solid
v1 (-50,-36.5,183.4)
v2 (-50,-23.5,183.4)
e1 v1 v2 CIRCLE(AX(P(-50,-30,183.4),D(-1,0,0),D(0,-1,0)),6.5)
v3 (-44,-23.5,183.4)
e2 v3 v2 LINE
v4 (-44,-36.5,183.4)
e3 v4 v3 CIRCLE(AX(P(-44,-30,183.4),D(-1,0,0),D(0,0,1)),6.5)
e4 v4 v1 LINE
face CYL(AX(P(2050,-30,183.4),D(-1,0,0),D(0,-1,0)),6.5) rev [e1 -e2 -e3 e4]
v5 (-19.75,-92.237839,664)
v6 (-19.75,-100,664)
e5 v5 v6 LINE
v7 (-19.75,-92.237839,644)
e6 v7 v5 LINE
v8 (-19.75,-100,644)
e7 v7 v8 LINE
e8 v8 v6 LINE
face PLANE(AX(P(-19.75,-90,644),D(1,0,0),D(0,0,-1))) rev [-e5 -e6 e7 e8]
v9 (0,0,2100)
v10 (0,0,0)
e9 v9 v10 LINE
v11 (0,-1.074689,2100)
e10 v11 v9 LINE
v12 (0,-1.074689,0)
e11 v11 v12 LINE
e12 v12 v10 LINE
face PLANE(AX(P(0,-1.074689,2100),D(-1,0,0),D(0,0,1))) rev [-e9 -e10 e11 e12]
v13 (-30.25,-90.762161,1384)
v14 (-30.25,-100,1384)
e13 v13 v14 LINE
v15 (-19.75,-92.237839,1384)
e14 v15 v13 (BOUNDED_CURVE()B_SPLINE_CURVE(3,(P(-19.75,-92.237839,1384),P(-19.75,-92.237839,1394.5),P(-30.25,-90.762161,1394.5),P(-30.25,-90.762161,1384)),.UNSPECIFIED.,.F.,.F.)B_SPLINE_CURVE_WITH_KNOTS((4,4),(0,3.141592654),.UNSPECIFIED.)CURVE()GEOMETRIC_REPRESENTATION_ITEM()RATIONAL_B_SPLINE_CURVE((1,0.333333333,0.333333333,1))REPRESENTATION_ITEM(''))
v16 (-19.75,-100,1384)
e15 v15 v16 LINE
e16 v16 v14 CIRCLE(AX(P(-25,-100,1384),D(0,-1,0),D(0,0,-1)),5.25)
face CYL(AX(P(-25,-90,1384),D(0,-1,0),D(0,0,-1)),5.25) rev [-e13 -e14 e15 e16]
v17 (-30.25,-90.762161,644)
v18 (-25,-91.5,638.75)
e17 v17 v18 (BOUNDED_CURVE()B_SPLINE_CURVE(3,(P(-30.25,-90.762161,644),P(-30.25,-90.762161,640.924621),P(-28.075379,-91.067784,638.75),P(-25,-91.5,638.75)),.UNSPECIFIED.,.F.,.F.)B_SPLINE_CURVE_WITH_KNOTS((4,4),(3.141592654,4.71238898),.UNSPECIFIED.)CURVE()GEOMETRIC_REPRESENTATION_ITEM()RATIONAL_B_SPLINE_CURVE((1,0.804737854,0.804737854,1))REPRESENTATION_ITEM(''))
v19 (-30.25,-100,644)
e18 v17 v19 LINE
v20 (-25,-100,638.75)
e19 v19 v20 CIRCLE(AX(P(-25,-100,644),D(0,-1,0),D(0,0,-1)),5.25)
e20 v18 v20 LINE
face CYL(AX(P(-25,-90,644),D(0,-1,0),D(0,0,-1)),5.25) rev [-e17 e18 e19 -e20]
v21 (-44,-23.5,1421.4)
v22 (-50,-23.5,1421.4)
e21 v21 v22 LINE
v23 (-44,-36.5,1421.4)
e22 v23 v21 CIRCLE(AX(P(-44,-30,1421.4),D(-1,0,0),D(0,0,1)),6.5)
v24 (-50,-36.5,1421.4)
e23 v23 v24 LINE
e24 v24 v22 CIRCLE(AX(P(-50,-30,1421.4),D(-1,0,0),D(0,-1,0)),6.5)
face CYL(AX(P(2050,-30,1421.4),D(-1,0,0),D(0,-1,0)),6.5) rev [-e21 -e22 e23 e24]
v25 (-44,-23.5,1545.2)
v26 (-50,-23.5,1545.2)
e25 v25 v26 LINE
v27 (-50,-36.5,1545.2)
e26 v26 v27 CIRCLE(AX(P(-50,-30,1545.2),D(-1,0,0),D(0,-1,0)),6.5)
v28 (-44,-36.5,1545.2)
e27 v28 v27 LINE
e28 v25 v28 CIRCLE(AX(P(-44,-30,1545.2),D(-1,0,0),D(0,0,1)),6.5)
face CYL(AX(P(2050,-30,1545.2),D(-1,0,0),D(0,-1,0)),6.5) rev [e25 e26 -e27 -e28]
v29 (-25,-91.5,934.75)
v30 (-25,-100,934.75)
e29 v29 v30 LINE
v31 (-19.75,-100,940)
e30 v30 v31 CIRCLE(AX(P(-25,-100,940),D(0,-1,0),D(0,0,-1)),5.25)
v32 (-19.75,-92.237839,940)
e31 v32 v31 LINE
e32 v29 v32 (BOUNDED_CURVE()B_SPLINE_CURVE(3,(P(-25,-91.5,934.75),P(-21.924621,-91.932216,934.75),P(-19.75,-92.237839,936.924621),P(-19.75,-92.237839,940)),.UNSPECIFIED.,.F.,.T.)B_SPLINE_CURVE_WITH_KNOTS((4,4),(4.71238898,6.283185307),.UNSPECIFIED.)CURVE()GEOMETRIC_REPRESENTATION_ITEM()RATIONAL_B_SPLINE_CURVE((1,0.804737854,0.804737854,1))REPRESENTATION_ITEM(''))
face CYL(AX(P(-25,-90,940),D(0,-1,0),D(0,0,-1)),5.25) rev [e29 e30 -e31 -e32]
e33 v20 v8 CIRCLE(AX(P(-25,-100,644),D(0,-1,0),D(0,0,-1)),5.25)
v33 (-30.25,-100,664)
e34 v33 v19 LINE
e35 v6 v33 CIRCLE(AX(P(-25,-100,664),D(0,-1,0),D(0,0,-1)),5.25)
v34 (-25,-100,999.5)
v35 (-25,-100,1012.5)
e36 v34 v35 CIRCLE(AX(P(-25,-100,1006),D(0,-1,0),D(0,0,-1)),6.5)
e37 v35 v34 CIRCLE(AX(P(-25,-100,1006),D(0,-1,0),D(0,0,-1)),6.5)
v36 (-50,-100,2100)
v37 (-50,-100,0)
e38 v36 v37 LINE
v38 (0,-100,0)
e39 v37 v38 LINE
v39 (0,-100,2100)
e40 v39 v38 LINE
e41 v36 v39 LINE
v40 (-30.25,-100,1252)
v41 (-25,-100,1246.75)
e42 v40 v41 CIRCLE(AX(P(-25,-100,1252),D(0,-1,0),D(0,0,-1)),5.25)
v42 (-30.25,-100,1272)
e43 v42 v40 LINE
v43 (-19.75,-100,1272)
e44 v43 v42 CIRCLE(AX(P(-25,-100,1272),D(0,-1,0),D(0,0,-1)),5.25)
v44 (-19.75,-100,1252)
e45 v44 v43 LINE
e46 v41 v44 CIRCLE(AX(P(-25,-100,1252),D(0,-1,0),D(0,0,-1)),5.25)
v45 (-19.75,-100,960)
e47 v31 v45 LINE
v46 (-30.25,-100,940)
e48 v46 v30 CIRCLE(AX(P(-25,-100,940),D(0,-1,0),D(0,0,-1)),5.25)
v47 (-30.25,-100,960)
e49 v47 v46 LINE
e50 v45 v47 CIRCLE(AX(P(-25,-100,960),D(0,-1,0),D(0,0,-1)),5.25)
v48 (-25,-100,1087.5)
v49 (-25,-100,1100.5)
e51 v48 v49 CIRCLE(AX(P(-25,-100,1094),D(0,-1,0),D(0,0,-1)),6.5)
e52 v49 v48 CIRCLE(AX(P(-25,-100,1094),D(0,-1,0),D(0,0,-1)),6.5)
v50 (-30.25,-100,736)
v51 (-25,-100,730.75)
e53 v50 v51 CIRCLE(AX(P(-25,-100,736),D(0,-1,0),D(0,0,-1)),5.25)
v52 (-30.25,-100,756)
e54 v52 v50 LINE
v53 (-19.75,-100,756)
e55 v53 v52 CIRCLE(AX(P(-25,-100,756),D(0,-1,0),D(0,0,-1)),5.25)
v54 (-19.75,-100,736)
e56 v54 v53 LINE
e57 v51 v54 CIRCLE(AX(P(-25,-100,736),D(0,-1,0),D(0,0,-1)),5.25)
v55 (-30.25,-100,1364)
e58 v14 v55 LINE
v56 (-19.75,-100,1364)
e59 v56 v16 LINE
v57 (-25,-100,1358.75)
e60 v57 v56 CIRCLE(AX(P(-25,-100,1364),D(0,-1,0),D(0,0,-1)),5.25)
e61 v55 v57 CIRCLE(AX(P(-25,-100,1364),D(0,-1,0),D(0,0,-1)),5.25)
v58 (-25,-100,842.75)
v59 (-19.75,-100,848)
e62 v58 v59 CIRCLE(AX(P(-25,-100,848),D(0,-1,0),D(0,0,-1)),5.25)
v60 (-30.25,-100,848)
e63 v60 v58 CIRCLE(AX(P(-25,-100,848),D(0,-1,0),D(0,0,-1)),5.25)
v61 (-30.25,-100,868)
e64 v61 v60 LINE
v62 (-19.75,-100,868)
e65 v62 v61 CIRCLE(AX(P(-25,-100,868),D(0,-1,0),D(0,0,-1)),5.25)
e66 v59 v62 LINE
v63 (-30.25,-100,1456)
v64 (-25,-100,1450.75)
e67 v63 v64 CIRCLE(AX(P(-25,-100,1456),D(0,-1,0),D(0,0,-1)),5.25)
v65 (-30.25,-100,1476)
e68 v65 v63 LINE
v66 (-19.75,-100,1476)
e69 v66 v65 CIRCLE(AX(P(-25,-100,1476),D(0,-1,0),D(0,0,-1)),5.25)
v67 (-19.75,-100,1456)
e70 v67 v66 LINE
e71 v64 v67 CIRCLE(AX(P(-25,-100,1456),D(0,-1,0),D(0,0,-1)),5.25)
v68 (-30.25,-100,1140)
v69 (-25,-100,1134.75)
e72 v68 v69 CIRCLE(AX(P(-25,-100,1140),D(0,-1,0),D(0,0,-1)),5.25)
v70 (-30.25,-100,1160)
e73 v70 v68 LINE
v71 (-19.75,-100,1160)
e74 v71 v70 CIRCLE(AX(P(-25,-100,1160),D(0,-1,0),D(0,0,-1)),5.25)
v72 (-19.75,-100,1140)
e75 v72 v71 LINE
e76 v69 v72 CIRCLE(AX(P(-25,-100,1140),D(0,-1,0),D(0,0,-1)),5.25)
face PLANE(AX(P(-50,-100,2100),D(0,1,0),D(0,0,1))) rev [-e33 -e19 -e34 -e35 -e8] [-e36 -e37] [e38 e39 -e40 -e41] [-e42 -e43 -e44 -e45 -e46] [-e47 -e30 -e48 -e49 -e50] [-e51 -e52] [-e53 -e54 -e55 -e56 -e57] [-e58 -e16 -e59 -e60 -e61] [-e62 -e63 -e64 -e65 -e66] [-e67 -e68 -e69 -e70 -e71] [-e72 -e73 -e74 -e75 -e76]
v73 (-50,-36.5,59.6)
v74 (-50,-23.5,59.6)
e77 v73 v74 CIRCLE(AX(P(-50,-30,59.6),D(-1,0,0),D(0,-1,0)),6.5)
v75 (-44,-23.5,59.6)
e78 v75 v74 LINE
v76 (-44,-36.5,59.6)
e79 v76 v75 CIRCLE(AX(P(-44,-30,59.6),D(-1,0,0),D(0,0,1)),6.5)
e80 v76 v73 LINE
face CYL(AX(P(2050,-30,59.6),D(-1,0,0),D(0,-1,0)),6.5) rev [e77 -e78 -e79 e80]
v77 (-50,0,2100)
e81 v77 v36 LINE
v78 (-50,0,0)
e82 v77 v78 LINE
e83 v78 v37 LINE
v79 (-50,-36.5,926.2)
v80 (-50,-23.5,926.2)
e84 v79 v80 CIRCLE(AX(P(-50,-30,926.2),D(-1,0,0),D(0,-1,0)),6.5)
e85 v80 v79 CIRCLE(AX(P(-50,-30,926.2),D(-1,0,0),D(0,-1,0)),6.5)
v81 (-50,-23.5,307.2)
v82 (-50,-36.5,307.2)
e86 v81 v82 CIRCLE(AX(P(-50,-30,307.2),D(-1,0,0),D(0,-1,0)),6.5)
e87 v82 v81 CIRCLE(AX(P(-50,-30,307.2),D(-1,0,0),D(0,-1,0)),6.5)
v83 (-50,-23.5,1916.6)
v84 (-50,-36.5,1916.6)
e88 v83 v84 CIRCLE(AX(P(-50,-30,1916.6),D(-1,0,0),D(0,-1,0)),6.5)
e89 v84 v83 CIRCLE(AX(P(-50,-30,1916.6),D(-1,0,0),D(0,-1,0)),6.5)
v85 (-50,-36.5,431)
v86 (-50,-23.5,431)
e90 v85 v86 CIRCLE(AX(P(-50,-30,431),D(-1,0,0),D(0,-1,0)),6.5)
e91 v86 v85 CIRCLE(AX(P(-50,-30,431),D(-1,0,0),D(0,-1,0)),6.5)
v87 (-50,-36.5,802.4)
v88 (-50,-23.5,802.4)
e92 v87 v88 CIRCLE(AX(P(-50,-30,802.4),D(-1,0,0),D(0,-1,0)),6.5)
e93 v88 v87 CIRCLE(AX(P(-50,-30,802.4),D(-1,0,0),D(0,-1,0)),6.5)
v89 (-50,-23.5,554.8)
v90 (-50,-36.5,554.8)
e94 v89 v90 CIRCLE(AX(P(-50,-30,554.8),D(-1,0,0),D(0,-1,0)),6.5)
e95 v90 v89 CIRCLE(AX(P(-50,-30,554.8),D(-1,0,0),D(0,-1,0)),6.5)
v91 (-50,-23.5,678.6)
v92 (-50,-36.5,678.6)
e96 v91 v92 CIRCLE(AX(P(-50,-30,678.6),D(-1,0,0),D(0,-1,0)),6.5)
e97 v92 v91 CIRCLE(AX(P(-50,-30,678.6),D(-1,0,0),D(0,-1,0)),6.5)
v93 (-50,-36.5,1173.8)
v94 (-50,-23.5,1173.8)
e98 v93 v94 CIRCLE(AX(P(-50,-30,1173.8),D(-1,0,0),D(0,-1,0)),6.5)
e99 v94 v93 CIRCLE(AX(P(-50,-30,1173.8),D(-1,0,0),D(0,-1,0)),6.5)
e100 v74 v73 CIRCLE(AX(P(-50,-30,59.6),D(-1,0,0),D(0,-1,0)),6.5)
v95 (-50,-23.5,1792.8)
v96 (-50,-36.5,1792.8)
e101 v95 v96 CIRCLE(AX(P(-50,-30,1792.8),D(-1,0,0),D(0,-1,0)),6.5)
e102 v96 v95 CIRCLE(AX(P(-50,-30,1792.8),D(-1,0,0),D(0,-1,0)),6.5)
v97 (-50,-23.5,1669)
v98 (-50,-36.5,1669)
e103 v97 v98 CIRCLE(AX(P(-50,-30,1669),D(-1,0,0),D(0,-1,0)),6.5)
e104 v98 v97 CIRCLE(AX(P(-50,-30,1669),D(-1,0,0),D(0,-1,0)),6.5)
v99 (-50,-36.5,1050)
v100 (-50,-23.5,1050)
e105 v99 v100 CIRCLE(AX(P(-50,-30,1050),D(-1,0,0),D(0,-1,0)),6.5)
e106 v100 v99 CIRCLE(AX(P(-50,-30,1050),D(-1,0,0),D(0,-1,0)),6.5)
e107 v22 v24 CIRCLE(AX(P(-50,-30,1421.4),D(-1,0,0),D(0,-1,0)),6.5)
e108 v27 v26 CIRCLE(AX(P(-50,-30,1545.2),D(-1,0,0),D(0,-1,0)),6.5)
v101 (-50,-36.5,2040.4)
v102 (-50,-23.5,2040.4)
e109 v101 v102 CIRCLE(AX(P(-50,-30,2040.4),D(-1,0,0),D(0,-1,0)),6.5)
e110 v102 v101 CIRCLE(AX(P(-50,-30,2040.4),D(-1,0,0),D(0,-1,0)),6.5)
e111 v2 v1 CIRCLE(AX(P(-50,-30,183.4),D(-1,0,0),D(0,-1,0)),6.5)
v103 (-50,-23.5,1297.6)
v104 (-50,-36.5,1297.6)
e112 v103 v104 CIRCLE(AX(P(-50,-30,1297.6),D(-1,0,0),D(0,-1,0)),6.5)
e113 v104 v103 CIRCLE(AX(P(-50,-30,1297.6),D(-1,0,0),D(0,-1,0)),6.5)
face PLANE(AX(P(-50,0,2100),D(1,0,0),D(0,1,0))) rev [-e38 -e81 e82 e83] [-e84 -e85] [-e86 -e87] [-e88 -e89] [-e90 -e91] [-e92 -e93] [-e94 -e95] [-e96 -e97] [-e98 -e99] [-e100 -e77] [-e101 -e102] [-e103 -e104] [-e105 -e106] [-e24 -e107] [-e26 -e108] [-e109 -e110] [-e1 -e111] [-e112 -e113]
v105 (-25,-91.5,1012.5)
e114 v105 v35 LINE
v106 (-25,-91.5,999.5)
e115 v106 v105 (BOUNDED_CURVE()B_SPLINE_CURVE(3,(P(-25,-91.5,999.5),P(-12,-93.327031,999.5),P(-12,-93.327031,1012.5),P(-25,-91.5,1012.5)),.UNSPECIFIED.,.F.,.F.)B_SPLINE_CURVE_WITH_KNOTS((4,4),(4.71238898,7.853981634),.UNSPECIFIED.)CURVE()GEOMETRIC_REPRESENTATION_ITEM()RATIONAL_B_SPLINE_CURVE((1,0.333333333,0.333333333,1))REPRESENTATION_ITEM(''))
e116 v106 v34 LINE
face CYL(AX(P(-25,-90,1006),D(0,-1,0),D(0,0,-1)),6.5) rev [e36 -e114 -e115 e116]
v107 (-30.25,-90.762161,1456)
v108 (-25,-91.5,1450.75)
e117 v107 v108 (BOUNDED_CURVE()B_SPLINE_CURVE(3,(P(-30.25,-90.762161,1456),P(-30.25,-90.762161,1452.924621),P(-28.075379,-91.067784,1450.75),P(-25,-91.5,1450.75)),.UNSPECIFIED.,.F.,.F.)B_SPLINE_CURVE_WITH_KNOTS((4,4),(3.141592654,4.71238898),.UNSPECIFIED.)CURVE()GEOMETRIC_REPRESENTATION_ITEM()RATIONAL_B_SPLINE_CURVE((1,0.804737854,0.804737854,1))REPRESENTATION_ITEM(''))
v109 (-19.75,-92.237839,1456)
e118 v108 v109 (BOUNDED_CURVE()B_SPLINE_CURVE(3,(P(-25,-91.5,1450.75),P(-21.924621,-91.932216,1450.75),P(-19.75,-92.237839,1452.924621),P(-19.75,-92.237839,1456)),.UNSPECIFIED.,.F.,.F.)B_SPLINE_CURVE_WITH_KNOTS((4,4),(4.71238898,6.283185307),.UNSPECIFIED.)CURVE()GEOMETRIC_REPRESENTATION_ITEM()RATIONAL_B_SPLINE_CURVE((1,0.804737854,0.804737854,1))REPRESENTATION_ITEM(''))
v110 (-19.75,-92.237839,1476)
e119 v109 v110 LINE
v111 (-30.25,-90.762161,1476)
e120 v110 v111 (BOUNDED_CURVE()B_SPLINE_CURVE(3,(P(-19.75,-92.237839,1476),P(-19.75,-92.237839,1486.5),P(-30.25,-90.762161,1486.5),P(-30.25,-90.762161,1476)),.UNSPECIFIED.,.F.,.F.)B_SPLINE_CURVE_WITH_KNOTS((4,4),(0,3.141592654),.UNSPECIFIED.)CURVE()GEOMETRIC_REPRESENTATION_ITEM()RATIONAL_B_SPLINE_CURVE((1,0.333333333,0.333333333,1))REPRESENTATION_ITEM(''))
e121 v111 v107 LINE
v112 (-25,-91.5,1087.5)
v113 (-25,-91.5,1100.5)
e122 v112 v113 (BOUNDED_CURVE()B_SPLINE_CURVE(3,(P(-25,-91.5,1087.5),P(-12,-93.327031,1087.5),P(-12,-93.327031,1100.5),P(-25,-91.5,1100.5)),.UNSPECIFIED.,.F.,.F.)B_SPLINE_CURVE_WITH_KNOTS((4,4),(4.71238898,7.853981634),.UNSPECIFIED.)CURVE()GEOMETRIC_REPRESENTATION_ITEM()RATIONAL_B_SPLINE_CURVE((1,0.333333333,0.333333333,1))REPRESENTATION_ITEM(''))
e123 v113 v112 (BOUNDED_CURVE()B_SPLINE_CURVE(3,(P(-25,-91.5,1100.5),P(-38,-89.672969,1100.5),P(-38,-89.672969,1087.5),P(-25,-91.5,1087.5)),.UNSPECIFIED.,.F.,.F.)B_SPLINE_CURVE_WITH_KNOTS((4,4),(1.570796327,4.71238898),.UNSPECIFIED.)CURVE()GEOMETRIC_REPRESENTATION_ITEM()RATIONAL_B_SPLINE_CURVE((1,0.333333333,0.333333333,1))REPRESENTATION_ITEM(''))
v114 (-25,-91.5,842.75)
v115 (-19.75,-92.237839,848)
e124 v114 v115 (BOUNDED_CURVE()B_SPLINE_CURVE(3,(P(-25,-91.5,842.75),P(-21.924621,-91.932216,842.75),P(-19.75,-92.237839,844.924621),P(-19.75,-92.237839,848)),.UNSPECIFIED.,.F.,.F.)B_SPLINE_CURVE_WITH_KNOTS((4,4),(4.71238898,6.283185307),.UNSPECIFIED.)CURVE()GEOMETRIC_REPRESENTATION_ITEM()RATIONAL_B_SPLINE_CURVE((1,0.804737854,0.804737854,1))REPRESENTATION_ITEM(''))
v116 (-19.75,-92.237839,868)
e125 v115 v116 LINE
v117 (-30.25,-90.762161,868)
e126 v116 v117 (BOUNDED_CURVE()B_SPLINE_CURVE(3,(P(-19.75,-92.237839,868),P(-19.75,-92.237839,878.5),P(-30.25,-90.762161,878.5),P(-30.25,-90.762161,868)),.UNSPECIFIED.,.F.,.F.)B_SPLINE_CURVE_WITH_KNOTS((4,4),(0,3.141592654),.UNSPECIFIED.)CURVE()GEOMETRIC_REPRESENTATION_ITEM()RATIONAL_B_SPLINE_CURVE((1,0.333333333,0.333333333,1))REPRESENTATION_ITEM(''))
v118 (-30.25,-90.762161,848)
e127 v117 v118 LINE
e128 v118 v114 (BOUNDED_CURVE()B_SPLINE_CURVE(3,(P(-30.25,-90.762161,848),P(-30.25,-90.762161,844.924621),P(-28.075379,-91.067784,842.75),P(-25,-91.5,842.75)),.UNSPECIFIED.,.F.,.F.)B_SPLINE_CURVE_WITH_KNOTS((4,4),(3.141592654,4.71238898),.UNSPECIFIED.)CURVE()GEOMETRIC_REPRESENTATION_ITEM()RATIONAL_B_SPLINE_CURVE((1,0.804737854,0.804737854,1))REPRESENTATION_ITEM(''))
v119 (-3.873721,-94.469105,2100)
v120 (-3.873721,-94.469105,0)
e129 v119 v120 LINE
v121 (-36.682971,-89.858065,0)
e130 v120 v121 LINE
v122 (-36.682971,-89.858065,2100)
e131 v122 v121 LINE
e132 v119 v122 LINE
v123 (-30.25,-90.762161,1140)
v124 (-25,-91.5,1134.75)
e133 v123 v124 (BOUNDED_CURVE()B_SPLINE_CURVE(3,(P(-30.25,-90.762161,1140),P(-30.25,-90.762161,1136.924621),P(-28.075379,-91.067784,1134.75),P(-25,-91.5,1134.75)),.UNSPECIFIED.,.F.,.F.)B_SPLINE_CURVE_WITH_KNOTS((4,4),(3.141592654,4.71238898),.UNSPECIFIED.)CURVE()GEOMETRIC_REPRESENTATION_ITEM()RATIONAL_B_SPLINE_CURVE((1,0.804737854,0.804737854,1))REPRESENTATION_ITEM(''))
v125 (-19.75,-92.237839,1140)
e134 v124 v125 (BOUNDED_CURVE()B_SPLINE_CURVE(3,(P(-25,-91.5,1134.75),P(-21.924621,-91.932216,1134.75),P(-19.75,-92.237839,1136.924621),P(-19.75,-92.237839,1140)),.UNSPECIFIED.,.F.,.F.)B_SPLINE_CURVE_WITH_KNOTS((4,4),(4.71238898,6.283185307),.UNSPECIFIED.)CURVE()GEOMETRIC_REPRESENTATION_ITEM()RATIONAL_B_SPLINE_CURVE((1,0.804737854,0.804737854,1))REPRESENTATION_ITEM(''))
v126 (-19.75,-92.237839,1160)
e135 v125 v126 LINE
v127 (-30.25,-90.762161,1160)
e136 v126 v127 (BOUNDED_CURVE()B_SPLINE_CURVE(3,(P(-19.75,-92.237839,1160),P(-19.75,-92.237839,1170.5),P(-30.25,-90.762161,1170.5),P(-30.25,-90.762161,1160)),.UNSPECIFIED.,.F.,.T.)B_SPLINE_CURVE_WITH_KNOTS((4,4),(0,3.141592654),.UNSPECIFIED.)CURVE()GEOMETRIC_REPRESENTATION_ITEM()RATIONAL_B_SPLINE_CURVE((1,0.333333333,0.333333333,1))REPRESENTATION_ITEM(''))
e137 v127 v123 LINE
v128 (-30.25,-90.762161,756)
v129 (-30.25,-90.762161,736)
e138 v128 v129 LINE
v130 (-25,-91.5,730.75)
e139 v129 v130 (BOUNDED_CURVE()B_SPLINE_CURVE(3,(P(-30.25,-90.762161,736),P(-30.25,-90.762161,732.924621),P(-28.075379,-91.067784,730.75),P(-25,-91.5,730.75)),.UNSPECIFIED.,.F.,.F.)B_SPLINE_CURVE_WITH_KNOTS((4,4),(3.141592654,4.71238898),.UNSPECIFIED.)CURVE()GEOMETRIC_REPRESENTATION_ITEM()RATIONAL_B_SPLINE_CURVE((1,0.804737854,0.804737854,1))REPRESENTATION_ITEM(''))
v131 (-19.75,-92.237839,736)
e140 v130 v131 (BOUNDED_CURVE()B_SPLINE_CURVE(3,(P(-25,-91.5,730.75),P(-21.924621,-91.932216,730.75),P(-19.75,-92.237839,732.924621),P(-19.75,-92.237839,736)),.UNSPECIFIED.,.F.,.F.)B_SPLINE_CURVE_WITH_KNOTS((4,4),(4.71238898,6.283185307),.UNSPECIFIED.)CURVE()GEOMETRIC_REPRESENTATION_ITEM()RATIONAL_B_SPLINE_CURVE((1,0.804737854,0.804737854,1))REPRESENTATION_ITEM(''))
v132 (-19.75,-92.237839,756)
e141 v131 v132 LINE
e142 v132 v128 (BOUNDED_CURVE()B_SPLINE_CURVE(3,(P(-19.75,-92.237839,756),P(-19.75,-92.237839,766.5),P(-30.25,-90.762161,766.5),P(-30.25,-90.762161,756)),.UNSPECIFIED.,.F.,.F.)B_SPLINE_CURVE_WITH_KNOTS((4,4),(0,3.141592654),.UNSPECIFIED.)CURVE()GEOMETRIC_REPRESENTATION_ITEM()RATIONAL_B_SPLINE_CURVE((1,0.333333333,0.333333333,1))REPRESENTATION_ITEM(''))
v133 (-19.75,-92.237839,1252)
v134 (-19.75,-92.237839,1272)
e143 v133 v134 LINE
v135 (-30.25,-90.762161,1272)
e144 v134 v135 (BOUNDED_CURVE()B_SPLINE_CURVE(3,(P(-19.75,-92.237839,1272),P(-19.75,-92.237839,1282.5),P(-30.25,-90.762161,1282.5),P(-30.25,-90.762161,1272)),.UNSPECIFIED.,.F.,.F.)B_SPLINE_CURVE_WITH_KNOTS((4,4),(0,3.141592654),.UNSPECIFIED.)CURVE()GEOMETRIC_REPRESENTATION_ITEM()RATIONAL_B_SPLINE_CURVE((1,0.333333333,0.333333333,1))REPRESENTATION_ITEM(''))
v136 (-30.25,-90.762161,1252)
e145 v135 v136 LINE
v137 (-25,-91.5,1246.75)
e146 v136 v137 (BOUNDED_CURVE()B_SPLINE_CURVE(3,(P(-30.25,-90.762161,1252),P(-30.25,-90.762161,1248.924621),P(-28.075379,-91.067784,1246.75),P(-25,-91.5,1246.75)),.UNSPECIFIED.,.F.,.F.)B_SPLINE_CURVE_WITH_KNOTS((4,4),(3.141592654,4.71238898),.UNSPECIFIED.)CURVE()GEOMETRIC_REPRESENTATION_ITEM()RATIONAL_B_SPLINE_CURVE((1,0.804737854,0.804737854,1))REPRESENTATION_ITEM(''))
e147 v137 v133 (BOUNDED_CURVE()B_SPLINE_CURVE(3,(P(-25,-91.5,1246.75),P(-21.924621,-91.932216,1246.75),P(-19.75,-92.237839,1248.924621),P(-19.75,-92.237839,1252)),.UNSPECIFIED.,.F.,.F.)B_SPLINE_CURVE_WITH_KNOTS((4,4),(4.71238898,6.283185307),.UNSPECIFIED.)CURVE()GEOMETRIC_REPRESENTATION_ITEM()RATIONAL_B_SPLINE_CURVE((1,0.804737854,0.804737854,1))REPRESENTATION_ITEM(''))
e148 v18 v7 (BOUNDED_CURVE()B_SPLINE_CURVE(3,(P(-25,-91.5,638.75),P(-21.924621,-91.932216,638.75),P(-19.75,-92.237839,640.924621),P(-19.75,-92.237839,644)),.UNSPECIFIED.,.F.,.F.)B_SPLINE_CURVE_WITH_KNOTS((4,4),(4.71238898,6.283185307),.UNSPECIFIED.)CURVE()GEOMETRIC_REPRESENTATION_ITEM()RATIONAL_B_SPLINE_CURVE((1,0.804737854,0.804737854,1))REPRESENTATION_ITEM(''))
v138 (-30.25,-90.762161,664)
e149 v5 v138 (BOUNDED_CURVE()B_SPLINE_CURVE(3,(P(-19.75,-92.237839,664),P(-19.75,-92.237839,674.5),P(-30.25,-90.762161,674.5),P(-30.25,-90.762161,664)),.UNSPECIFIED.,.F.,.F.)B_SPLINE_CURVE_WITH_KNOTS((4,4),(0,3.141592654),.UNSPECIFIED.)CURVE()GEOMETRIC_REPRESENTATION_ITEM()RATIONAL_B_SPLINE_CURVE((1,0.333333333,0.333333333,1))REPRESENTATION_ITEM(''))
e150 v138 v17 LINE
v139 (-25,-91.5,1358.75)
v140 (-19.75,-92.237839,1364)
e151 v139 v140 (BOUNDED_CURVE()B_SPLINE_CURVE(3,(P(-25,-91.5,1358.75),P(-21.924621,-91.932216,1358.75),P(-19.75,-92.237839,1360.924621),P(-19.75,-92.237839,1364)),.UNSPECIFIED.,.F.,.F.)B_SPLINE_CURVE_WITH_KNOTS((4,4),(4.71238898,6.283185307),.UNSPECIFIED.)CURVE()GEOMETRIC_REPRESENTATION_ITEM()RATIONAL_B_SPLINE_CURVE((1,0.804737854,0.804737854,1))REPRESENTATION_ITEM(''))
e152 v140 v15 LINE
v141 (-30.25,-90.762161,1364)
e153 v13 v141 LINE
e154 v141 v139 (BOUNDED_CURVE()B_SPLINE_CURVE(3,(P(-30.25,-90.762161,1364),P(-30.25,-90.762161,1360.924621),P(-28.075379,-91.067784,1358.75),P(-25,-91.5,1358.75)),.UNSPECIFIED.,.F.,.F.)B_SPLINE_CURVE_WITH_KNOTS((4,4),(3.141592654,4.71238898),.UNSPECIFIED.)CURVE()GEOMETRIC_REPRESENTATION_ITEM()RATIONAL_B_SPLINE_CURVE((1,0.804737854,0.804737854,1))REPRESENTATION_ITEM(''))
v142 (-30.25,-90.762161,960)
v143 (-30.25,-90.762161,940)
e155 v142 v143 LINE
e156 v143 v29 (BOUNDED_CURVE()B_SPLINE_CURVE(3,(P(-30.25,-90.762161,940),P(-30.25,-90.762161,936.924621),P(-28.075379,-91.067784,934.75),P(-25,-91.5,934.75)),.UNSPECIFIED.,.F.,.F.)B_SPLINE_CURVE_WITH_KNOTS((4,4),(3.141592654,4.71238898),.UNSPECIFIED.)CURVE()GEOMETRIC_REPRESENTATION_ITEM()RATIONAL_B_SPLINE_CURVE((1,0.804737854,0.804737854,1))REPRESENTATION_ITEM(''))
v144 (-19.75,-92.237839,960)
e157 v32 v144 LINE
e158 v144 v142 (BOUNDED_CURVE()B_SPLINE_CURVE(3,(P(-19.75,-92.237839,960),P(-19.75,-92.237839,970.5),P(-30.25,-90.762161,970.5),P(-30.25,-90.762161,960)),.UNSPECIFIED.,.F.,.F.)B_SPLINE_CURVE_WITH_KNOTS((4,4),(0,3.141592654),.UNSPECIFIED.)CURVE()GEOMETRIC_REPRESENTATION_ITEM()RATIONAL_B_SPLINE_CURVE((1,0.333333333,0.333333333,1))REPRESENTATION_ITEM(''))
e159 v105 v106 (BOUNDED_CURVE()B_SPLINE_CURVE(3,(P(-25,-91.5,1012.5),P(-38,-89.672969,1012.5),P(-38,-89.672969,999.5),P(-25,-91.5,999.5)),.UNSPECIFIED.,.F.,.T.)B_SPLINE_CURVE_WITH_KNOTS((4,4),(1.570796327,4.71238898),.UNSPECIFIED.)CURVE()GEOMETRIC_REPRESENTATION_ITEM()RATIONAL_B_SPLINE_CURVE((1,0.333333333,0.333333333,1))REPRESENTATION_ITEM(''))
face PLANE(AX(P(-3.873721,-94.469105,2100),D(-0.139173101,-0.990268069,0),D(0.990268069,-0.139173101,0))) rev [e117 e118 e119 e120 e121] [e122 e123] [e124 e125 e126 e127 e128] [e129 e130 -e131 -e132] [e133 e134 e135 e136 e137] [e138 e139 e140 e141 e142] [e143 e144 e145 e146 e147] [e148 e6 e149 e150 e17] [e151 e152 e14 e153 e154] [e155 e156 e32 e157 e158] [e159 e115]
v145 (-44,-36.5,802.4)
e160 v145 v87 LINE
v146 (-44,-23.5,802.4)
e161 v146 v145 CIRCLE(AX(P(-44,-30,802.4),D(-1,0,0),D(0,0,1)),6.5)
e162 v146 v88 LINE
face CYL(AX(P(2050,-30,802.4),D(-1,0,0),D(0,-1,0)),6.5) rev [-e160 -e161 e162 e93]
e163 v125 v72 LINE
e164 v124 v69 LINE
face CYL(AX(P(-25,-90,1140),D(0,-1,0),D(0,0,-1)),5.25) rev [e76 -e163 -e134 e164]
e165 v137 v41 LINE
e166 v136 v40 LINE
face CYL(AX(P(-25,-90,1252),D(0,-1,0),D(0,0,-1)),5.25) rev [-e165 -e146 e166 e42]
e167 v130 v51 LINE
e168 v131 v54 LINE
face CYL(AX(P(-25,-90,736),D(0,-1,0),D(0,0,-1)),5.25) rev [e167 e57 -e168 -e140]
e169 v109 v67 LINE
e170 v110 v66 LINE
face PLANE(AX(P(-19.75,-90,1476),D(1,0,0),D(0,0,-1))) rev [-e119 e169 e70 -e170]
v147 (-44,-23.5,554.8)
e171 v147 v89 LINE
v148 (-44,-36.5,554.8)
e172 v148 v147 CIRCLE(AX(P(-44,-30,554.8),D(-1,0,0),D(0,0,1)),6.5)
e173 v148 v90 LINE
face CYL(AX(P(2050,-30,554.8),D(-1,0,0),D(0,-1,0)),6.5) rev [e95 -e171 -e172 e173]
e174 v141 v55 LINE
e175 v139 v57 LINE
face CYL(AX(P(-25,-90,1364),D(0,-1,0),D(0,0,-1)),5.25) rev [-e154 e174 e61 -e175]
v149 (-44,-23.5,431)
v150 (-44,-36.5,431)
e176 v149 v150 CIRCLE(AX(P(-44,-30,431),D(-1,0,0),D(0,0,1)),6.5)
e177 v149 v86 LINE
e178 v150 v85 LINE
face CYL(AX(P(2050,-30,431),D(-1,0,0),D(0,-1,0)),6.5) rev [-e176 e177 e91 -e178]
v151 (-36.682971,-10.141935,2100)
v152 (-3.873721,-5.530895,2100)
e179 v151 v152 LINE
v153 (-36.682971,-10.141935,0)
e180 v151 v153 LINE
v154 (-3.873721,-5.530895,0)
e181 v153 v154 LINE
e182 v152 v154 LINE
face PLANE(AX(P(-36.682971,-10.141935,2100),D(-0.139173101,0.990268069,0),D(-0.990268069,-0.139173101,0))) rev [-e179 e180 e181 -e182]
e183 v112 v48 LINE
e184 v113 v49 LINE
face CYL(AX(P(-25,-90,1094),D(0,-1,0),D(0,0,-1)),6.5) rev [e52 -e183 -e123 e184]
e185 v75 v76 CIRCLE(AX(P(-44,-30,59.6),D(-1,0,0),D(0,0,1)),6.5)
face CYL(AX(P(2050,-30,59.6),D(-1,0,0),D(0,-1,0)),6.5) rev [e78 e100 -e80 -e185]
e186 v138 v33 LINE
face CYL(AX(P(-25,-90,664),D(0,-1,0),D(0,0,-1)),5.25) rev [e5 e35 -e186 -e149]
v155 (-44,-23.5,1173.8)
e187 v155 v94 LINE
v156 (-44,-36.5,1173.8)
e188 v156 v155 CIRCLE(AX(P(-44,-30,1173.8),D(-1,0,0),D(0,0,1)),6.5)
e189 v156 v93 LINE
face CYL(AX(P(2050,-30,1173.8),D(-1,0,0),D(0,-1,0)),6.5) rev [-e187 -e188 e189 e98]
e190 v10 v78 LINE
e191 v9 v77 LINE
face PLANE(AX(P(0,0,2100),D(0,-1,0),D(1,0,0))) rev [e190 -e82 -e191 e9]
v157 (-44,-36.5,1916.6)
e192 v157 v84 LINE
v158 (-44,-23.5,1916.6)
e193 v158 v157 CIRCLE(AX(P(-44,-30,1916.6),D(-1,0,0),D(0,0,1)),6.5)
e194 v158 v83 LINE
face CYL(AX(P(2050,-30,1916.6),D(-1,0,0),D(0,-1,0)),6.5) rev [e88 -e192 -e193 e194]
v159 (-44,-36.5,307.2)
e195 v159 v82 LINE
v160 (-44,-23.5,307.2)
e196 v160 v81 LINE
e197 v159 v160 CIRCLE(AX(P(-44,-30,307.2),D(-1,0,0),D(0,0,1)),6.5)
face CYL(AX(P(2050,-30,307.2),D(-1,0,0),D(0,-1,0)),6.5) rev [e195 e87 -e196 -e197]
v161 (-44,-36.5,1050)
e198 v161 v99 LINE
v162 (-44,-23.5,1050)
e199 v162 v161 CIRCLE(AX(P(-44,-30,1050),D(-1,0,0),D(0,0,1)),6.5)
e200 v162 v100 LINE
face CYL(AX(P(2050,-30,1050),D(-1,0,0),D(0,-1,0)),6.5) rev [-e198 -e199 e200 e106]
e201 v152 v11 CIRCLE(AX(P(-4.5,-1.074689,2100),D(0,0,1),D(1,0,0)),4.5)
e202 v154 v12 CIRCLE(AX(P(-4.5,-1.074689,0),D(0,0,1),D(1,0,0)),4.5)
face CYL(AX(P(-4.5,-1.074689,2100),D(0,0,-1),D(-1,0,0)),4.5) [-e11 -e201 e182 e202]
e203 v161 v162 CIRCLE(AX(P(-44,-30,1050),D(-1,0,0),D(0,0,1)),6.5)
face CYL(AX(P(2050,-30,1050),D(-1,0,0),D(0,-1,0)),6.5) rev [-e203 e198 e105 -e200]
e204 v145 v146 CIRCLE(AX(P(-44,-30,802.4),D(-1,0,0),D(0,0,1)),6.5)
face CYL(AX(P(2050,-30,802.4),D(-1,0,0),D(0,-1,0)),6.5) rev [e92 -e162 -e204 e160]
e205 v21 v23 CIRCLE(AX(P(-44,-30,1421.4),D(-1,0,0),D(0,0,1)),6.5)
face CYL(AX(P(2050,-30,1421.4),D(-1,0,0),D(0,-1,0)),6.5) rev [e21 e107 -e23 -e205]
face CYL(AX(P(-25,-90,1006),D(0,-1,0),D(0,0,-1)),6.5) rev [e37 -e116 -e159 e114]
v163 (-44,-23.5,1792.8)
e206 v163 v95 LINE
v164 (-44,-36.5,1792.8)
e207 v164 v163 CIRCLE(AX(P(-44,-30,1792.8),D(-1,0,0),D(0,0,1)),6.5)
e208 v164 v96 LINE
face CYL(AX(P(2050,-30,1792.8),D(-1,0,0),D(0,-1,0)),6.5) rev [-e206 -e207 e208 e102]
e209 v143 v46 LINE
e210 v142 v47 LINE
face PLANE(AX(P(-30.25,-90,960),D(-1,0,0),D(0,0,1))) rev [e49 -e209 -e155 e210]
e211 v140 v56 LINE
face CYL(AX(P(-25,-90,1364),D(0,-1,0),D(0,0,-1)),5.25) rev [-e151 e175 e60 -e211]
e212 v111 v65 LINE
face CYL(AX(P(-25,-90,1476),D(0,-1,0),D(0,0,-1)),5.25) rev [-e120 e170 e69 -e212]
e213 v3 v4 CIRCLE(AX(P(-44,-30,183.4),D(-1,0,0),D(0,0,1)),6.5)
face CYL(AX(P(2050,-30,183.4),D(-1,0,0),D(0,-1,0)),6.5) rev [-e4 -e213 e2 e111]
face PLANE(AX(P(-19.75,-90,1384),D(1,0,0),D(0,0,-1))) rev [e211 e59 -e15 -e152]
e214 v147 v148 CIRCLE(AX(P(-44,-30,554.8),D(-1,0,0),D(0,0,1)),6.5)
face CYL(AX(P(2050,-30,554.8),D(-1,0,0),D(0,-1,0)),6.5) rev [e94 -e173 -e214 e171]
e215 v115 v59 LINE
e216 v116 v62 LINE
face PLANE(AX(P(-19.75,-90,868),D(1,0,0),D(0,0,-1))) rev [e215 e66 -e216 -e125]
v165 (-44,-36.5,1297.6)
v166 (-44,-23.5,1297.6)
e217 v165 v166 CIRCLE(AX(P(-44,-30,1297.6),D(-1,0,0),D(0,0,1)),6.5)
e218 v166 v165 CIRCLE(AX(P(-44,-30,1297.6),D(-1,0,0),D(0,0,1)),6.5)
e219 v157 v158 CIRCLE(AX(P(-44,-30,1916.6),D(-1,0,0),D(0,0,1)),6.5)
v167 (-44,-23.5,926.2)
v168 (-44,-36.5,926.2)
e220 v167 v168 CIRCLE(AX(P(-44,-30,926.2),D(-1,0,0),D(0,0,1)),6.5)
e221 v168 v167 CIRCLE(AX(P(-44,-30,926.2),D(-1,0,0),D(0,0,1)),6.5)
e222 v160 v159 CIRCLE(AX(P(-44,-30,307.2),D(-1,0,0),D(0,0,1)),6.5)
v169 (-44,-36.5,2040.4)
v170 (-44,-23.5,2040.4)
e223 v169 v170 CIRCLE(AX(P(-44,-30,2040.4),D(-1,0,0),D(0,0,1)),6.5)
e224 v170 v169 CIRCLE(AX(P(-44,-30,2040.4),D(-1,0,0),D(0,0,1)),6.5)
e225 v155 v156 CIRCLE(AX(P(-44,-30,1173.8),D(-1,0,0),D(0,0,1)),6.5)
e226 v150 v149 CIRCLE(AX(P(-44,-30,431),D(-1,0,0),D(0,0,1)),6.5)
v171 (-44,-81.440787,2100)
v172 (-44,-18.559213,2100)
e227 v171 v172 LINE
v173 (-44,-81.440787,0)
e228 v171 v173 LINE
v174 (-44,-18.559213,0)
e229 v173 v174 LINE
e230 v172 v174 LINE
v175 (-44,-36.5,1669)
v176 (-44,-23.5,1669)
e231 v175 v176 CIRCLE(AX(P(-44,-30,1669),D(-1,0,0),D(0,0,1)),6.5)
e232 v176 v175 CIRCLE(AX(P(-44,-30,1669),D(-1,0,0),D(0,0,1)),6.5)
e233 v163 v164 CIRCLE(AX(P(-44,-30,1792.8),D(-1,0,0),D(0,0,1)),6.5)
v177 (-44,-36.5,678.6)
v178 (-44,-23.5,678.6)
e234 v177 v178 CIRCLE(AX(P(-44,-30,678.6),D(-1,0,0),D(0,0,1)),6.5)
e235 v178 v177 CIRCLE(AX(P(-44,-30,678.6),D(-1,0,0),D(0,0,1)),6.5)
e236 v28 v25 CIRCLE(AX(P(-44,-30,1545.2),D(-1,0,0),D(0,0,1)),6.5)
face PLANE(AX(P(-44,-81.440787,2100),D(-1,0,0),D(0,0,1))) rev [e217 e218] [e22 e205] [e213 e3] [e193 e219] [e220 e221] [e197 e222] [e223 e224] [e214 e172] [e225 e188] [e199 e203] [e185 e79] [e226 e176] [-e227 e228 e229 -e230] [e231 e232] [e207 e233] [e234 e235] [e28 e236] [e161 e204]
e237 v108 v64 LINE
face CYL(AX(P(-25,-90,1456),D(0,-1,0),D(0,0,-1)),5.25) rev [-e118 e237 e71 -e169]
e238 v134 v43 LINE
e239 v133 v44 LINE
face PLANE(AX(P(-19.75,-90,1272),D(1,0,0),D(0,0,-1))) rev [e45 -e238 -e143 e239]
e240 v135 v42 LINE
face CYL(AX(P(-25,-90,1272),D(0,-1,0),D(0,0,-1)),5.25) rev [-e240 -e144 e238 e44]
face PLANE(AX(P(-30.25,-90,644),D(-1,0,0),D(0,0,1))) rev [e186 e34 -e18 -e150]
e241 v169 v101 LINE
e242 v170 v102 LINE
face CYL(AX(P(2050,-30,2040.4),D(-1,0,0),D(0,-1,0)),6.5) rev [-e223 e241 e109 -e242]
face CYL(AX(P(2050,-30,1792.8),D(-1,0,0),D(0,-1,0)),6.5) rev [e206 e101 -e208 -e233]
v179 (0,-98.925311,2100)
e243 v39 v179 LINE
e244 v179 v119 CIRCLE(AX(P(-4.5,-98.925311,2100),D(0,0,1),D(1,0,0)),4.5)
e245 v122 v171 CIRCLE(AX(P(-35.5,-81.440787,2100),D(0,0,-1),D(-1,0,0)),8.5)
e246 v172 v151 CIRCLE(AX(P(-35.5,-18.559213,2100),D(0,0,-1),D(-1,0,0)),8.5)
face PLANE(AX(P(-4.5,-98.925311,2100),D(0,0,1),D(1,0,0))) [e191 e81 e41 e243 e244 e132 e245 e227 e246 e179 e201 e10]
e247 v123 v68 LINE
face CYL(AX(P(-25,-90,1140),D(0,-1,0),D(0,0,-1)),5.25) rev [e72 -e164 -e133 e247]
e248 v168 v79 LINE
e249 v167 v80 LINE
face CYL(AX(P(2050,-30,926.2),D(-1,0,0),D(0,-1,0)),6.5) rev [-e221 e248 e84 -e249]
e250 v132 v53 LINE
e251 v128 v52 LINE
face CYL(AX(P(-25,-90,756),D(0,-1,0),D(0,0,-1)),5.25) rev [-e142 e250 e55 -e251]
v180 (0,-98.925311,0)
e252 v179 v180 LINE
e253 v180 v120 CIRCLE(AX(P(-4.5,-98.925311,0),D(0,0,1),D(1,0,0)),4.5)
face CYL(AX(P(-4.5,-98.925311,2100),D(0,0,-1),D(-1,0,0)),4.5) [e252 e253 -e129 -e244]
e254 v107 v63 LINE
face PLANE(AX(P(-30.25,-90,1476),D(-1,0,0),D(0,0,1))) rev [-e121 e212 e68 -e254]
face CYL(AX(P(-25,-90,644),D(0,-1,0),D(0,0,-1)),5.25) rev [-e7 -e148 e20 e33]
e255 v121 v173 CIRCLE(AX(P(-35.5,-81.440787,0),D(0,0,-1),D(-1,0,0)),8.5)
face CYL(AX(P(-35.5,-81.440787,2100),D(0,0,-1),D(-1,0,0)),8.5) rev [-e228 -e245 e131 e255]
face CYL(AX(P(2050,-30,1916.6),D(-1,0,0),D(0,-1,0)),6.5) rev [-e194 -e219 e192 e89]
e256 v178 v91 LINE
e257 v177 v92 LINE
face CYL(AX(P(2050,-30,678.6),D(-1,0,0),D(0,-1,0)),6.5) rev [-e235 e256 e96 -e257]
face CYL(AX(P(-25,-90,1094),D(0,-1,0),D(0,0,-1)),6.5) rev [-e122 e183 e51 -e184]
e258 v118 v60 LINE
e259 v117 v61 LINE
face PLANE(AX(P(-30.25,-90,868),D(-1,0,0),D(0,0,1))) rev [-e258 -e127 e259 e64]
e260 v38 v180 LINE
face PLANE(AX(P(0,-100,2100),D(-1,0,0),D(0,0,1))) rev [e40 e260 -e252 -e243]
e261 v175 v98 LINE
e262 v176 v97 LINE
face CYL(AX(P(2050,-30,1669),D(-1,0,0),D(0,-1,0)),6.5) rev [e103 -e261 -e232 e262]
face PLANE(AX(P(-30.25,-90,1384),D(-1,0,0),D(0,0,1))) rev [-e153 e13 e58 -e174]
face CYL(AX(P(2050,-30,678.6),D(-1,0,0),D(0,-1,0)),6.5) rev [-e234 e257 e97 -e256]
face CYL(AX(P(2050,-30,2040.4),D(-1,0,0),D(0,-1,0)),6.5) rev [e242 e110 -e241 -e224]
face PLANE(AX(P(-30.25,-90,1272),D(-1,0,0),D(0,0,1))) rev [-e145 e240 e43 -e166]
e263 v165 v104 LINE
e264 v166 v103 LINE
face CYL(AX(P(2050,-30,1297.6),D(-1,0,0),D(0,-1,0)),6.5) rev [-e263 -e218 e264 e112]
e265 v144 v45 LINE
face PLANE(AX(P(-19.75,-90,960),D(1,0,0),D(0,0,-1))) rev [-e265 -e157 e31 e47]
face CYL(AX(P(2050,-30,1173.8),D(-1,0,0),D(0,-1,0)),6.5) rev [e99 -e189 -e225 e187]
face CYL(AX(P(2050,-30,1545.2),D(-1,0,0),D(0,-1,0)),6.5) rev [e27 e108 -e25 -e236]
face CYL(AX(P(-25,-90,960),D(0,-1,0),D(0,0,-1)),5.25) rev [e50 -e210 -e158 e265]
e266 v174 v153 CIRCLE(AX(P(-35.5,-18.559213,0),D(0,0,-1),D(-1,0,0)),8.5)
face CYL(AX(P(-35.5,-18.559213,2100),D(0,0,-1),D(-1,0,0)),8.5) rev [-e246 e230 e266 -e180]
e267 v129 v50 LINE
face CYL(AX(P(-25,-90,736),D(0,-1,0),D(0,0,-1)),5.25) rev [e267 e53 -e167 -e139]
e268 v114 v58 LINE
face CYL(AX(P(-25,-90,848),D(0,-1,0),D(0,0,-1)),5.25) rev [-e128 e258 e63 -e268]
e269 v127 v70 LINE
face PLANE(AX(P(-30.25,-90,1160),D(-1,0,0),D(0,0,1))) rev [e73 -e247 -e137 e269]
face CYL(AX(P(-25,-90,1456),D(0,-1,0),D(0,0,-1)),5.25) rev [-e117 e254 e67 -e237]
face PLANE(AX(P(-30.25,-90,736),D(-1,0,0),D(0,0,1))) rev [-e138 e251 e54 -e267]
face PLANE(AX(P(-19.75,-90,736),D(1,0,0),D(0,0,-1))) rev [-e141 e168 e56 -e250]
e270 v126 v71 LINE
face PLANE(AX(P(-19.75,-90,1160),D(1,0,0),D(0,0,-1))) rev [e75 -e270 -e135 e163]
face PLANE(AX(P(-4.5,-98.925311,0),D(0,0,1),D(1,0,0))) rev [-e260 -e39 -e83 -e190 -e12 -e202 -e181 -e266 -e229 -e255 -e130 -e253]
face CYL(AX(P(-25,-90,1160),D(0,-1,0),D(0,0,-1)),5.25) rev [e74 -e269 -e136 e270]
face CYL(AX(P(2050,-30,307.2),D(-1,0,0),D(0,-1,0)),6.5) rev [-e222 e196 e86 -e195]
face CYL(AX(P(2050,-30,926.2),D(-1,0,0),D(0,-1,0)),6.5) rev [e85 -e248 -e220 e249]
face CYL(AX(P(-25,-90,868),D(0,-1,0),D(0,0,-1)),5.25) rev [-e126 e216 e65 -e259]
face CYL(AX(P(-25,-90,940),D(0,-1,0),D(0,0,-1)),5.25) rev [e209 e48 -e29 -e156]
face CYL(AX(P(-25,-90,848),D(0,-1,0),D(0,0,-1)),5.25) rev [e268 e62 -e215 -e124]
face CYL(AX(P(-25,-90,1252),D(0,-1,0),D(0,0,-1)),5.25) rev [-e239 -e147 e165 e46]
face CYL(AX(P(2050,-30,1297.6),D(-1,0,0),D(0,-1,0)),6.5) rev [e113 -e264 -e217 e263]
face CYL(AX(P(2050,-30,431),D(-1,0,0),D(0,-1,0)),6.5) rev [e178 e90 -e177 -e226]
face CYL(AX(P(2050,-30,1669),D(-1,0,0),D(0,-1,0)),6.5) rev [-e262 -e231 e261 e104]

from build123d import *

# Parameters (mm, degrees)
EXTRUDE_1_DEPTH     = 2100
SKETCH_2_R          = 6.5
CUT_EXTRUDE_1_DEPTH = 2100
SKETCH_6_R          = 6.5
CUT_EXTRUDE_3_DEPTH = 10


with BuildPart() as part:
    # 草图1 → 凸台-拉伸1 (new body)
    with BuildSketch(Plane.XY):
        with BuildLine():
            Line((0, 0), (-50, 0))
            Line((-50, 0), (-50, -100))
            Line((-50, -100), (0, -100))
            Line((0, -100), (0, -98.925311188))
            ThreePointArc((0, -98.925311188), (-1.103806889, -95.973045557), (-3.873721046, -94.469104878))
            Line((-3.873721046, -94.469104878), (-36.682971358, -89.858065454))
            ThreePointArc((-36.682971358, -89.858065454), (-41.915031432, -87.017288616), (-44, -81.440786869))
            Line((-44, -81.440786869), (-44, -18.559213131))
            ThreePointArc((-44, -18.559213131), (-41.915031432, -12.982711384), (-36.682971358, -10.141934546))
            Line((-36.682971358, -10.141934546), (-3.873721046, -5.530895122))
            ThreePointArc((-3.873721046, -5.530895122), (-1.103806889, -4.026954443), (0, -1.074688812))
            Line((0, -1.074688812), (0, 0))
        make_face()
    extrude(amount=EXTRUDE_1_DEPTH)

    # 草图2 → 切除-拉伸1 (cut)
    with BuildSketch(Plane.ZY.offset(50)):
        with Locations(Location((59.6, -30, 0), (0, 0, 270))):
            Circle(SKETCH_2_R)
        with Locations(Location((183.4, -30, 0), (0, 0, 270))):
            Circle(SKETCH_2_R)
        with Locations(Location((307.2, -30, 0), (0, 0, 270))):
            Circle(SKETCH_2_R)
        with Locations(Location((431, -30, 0), (0, 0, 270))):
            Circle(SKETCH_2_R)
        with Locations(Location((554.8, -30, 0), (0, 0, 270))):
            Circle(SKETCH_2_R)
        with Locations(Location((678.6, -30, 0), (0, 0, 270))):
            Circle(SKETCH_2_R)
        with Locations(Location((802.4, -30, 0), (0, 0, 270))):
            Circle(SKETCH_2_R)
        with Locations(Location((926.2, -30, 0), (0, 0, 270))):
            Circle(SKETCH_2_R)
        with Locations(Location((1050, -30, 0), (0, 0, 270))):
            Circle(SKETCH_2_R)
        with Locations(Location((1173.8, -30, 0), (0, 0, 270))):
            Circle(SKETCH_2_R)
        with Locations(Location((1297.6, -30, 0), (0, 0, 270))):
            Circle(SKETCH_2_R)
        with Locations(Location((1421.4, -30, 0), (0, 0, 270))):
            Circle(SKETCH_2_R)
        with Locations(Location((1545.2, -30, 0), (0, 0, 270))):
            Circle(SKETCH_2_R)
        with Locations(Location((1669, -30, 0), (0, 0, 270))):
            Circle(SKETCH_2_R)
        with Locations(Location((1792.8, -30, 0), (0, 0, 270))):
            Circle(SKETCH_2_R)
        with Locations(Location((1916.6, -30, 0), (0, 0, 270))):
            Circle(SKETCH_2_R)
        with Locations(Location((2040.4, -30, 0), (0, 0, 270))):
            Circle(SKETCH_2_R)
    extrude(amount=-CUT_EXTRUDE_1_DEPTH, mode=Mode.SUBTRACT)

    # 草图6 → 切除-拉伸3 (cut)
    with BuildSketch(Plane.XZ.offset(100)):
        with Locations(Location((-25, 1006, 0), (0, 0, 270))):
            Circle(SKETCH_6_R)
        with Locations(Location((-25, 1094, 0), (0, 0, 270))):
            Circle(SKETCH_6_R)
        with BuildLine():
            Line((-30.25, 644), (-30.25, 664))
            ThreePointArc((-30.25, 664), (-25, 669.25), (-19.75, 664))
            Line((-19.75, 664), (-19.75, 644))
            ThreePointArc((-19.75, 644), (-25, 638.75), (-30.25, 644))
        make_face()
        with BuildLine():
            Line((-30.25, 736), (-30.25, 756))
            ThreePointArc((-30.25, 756), (-25, 761.25), (-19.75, 756))
            Line((-19.75, 756), (-19.75, 736))
            ThreePointArc((-19.75, 736), (-25, 730.75), (-30.25, 736))
        make_face()
        with BuildLine():
            Line((-19.75, 868), (-19.75, 848))
            ThreePointArc((-19.75, 848), (-25, 842.75), (-30.25, 848))
            Line((-30.25, 848), (-30.25, 868))
            ThreePointArc((-30.25, 868), (-25, 873.25), (-19.75, 868))
        make_face()
        with BuildLine():
            Line((-19.75, 960), (-19.75, 940))
            ThreePointArc((-19.75, 940), (-25, 934.75), (-30.25, 940))
            Line((-30.25, 940), (-30.25, 960))
            ThreePointArc((-30.25, 960), (-25, 965.25), (-19.75, 960))
        make_face()
        with BuildLine():
            Line((-19.75, 1272), (-19.75, 1252))
            ThreePointArc((-19.75, 1252), (-25, 1246.75), (-30.25, 1252))
            Line((-30.25, 1252), (-30.25, 1272))
            ThreePointArc((-30.25, 1272), (-25, 1277.25), (-19.75, 1272))
        make_face()
        with BuildLine():
            Line((-19.75, 1476), (-19.75, 1456))
            ThreePointArc((-19.75, 1456), (-25, 1450.75), (-30.25, 1456))
            Line((-30.25, 1456), (-30.25, 1476))
            ThreePointArc((-30.25, 1476), (-25, 1481.25), (-19.75, 1476))
        make_face()
        with BuildLine():
            Line((-19.75, 1384), (-19.75, 1364))
            ThreePointArc((-19.75, 1364), (-25, 1358.75), (-30.25, 1364))
            Line((-30.25, 1364), (-30.25, 1384))
            ThreePointArc((-30.25, 1384), (-25, 1389.25), (-19.75, 1384))
        make_face()
        with BuildLine():
            Line((-19.75, 1160), (-19.75, 1140))
            ThreePointArc((-19.75, 1140), (-25, 1134.75), (-30.25, 1140))
            Line((-30.25, 1140), (-30.25, 1160))
            ThreePointArc((-30.25, 1160), (-25, 1165.25), (-19.75, 1160))
        make_face()
    extrude(amount=-CUT_EXTRUDE_3_DEPTH, mode=Mode.SUBTRACT)


solid = part.part
